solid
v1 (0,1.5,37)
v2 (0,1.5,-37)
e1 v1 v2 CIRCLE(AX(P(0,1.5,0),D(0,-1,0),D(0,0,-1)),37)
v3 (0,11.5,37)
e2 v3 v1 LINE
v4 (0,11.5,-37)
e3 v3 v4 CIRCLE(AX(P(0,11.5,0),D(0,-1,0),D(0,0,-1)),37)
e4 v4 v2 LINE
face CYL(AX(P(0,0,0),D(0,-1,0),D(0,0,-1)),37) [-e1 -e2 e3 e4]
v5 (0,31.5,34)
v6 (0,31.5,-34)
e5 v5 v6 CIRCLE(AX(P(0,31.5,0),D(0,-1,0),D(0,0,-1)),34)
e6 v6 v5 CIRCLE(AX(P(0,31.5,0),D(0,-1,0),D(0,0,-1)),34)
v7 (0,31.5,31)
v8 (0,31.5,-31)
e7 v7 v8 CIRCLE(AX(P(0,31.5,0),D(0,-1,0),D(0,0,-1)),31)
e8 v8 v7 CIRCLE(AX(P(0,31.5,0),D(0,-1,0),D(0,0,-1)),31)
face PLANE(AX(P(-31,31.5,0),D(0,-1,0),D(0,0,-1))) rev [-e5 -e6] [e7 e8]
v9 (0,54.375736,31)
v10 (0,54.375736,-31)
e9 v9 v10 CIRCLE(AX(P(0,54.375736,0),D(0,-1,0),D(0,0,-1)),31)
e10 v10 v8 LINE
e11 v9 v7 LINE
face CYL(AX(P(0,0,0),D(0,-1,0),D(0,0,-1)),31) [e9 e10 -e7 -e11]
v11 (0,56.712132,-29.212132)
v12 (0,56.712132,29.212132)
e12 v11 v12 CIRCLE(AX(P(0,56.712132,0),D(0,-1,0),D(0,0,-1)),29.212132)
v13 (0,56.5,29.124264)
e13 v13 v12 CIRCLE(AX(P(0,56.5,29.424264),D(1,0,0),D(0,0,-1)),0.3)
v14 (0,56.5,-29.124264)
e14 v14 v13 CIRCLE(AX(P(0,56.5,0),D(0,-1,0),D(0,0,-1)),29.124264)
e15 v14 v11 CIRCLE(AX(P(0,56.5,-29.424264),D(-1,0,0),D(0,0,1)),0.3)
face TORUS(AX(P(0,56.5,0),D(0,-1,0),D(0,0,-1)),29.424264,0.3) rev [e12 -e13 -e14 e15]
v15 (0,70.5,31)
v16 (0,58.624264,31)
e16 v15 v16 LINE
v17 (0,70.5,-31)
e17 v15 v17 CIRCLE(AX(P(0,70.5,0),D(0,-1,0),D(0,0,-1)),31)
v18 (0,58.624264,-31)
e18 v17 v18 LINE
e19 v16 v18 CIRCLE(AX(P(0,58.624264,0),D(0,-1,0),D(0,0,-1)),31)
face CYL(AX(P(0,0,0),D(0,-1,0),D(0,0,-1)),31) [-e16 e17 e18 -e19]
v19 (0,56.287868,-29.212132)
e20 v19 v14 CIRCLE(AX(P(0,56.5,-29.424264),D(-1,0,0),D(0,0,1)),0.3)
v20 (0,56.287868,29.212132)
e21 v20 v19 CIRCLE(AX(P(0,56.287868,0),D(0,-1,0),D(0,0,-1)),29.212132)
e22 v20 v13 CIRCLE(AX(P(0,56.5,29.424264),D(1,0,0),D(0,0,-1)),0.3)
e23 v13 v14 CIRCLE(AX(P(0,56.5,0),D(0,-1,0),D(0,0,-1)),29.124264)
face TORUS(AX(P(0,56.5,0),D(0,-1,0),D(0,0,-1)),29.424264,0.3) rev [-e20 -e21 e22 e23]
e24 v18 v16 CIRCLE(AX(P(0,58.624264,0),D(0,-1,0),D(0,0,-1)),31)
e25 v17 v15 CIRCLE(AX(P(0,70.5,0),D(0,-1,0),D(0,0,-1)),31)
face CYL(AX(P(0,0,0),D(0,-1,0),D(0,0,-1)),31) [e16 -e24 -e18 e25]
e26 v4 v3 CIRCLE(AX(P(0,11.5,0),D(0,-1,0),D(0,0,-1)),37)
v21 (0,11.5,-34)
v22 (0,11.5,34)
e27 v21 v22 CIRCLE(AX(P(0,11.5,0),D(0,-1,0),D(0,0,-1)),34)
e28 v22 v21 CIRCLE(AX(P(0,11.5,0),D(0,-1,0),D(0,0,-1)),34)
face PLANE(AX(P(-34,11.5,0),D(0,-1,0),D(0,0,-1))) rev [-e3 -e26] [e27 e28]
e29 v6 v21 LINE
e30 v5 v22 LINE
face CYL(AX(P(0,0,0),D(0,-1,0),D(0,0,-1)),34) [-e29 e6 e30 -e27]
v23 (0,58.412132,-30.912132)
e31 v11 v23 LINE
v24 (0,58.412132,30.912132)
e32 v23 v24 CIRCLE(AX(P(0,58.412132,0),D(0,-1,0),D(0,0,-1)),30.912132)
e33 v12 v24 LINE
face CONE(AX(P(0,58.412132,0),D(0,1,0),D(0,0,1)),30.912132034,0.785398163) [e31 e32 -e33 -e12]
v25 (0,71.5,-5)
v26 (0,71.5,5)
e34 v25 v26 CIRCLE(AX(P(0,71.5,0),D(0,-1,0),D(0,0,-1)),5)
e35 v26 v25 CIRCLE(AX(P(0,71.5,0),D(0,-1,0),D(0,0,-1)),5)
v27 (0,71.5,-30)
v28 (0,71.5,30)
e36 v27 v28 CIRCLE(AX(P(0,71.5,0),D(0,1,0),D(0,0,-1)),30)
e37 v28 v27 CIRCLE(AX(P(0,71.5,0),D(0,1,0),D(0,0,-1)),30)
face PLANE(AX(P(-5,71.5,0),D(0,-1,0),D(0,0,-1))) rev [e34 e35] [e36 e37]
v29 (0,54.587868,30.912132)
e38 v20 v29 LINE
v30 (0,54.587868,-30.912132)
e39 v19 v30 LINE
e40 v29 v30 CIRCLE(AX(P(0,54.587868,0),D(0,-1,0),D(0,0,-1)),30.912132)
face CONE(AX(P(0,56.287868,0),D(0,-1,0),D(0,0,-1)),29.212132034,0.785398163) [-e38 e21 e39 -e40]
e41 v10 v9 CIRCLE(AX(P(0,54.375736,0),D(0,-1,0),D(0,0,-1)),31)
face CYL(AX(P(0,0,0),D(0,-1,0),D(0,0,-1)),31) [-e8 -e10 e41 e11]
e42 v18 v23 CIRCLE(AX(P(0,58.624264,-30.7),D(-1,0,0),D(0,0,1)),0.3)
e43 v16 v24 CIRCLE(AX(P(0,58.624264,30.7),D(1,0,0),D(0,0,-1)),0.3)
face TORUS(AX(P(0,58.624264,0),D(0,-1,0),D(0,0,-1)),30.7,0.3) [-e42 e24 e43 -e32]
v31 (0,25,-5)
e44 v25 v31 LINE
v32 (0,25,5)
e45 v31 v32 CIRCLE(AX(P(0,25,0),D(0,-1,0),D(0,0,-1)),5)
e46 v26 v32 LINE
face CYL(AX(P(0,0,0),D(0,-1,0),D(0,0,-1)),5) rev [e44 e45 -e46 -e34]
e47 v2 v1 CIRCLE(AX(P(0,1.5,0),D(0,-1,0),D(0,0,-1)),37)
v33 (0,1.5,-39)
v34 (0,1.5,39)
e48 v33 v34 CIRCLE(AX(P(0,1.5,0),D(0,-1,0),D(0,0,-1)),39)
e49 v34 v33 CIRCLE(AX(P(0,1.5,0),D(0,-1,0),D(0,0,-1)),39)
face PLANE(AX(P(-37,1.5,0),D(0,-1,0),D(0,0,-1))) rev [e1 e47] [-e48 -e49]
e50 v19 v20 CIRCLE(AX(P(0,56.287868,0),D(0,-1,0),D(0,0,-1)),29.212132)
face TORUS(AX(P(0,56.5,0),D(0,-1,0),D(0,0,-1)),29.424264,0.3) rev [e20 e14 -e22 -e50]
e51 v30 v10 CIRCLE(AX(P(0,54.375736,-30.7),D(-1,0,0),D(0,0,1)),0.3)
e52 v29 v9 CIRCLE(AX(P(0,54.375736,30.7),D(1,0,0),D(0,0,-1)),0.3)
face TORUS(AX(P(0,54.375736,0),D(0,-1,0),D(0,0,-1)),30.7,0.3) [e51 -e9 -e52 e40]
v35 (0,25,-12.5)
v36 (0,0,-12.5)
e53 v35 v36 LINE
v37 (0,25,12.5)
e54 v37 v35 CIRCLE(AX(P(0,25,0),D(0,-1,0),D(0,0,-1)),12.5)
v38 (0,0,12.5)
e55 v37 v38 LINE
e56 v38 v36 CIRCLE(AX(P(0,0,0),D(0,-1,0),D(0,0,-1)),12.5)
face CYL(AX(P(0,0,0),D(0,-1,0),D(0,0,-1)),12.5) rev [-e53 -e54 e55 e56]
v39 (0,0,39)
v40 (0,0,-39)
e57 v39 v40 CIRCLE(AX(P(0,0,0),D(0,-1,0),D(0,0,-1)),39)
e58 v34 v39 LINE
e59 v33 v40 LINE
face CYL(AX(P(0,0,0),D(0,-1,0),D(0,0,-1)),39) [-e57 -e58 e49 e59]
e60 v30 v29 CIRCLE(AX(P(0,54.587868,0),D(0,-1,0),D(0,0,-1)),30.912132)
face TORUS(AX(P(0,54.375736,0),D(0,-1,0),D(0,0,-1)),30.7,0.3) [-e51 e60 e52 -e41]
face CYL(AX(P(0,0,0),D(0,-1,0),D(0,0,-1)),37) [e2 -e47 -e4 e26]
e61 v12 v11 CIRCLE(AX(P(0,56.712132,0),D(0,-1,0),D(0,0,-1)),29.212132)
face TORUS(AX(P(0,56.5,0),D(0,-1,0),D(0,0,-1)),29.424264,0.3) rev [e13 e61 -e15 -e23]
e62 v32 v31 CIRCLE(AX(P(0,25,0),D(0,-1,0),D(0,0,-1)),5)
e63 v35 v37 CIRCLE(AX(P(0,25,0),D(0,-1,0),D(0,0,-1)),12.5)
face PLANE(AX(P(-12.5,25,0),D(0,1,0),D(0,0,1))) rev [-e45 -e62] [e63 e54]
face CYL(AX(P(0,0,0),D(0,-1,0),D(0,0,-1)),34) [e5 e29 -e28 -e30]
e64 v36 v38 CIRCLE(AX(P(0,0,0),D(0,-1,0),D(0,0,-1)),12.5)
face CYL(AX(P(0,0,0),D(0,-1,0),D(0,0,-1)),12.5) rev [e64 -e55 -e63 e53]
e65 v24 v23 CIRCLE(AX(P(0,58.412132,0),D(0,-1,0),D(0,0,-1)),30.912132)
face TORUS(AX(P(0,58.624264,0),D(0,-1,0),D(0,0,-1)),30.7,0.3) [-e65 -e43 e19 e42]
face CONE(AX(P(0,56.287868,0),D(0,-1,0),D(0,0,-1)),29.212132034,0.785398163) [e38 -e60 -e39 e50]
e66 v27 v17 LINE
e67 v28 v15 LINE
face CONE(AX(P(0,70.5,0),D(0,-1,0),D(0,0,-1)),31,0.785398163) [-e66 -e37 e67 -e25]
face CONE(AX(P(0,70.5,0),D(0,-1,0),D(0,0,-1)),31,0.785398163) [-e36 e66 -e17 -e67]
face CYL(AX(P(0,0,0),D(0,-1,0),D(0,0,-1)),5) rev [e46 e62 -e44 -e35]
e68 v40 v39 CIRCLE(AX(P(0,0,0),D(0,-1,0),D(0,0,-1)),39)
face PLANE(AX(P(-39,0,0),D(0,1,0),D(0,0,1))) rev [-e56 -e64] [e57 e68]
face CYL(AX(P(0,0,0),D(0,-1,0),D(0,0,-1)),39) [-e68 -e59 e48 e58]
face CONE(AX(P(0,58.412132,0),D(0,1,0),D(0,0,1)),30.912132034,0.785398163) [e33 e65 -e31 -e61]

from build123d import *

# Parameters (mm, degrees)
CHAMFER_1_SIZE = 1


with BuildPart() as part:
    # 草图1 → 旋转1 (revolve)
    with BuildSketch(Plane.XY, mode=Mode.PRIVATE) as revolve_1_sk:
        with BuildLine():
            Line((-12.5, 0), (-12.5, 25))
            Line((-12.5, 25), (-5, 25))
            Line((-5, 25), (-5, 71.5))
            Line((-5, 71.5), (-31, 71.5))
            Line((-31, 71.5), (-31, 58.624264069))
            ThreePointArc((-31, 58.624264069), (-30.97716386, 58.509459039), (-30.912132034, 58.412132034))
            Line((-30.912132034, 58.412132034), (-29.212132034, 56.712132034))
            ThreePointArc((-29.212132034, 56.712132034), (-29.124264069, 56.5), (-29.212132034, 56.287867966))
            Line((-29.212132034, 56.287867966), (-30.912132034, 54.587867966))
            ThreePointArc((-30.912132034, 54.587867966), (-30.97716386, 54.490540961), (-31, 54.375735931))
            Line((-31, 54.375735931), (-31, 31.5))
            Line((-31, 31.5), (-34, 31.5))
            Line((-34, 31.5), (-34, 11.5))
            Line((-34, 11.5), (-37, 11.5))
            Line((-37, 11.5), (-37, 1.5))
            Line((-37, 1.5), (-39, 1.5))
            Line((-39, 1.5), (-39, 0))
            Line((-39, 0), (-12.5, 0))
        make_face()
    revolve(revolve_1_sk.sketch.rotate(Axis((0, 0, 0), (0, 1, 0)), 270), axis=Axis((0, 0, 0), (0, 1, 0)))

    # 倒角1
    chamfer_1_edges = [part.edges().sort_by_distance(p)[0] for p in [
        (0, 71.5, 31),
    ]]
    chamfer(chamfer_1_edges, length=CHAMFER_1_SIZE)


solid = part.part
